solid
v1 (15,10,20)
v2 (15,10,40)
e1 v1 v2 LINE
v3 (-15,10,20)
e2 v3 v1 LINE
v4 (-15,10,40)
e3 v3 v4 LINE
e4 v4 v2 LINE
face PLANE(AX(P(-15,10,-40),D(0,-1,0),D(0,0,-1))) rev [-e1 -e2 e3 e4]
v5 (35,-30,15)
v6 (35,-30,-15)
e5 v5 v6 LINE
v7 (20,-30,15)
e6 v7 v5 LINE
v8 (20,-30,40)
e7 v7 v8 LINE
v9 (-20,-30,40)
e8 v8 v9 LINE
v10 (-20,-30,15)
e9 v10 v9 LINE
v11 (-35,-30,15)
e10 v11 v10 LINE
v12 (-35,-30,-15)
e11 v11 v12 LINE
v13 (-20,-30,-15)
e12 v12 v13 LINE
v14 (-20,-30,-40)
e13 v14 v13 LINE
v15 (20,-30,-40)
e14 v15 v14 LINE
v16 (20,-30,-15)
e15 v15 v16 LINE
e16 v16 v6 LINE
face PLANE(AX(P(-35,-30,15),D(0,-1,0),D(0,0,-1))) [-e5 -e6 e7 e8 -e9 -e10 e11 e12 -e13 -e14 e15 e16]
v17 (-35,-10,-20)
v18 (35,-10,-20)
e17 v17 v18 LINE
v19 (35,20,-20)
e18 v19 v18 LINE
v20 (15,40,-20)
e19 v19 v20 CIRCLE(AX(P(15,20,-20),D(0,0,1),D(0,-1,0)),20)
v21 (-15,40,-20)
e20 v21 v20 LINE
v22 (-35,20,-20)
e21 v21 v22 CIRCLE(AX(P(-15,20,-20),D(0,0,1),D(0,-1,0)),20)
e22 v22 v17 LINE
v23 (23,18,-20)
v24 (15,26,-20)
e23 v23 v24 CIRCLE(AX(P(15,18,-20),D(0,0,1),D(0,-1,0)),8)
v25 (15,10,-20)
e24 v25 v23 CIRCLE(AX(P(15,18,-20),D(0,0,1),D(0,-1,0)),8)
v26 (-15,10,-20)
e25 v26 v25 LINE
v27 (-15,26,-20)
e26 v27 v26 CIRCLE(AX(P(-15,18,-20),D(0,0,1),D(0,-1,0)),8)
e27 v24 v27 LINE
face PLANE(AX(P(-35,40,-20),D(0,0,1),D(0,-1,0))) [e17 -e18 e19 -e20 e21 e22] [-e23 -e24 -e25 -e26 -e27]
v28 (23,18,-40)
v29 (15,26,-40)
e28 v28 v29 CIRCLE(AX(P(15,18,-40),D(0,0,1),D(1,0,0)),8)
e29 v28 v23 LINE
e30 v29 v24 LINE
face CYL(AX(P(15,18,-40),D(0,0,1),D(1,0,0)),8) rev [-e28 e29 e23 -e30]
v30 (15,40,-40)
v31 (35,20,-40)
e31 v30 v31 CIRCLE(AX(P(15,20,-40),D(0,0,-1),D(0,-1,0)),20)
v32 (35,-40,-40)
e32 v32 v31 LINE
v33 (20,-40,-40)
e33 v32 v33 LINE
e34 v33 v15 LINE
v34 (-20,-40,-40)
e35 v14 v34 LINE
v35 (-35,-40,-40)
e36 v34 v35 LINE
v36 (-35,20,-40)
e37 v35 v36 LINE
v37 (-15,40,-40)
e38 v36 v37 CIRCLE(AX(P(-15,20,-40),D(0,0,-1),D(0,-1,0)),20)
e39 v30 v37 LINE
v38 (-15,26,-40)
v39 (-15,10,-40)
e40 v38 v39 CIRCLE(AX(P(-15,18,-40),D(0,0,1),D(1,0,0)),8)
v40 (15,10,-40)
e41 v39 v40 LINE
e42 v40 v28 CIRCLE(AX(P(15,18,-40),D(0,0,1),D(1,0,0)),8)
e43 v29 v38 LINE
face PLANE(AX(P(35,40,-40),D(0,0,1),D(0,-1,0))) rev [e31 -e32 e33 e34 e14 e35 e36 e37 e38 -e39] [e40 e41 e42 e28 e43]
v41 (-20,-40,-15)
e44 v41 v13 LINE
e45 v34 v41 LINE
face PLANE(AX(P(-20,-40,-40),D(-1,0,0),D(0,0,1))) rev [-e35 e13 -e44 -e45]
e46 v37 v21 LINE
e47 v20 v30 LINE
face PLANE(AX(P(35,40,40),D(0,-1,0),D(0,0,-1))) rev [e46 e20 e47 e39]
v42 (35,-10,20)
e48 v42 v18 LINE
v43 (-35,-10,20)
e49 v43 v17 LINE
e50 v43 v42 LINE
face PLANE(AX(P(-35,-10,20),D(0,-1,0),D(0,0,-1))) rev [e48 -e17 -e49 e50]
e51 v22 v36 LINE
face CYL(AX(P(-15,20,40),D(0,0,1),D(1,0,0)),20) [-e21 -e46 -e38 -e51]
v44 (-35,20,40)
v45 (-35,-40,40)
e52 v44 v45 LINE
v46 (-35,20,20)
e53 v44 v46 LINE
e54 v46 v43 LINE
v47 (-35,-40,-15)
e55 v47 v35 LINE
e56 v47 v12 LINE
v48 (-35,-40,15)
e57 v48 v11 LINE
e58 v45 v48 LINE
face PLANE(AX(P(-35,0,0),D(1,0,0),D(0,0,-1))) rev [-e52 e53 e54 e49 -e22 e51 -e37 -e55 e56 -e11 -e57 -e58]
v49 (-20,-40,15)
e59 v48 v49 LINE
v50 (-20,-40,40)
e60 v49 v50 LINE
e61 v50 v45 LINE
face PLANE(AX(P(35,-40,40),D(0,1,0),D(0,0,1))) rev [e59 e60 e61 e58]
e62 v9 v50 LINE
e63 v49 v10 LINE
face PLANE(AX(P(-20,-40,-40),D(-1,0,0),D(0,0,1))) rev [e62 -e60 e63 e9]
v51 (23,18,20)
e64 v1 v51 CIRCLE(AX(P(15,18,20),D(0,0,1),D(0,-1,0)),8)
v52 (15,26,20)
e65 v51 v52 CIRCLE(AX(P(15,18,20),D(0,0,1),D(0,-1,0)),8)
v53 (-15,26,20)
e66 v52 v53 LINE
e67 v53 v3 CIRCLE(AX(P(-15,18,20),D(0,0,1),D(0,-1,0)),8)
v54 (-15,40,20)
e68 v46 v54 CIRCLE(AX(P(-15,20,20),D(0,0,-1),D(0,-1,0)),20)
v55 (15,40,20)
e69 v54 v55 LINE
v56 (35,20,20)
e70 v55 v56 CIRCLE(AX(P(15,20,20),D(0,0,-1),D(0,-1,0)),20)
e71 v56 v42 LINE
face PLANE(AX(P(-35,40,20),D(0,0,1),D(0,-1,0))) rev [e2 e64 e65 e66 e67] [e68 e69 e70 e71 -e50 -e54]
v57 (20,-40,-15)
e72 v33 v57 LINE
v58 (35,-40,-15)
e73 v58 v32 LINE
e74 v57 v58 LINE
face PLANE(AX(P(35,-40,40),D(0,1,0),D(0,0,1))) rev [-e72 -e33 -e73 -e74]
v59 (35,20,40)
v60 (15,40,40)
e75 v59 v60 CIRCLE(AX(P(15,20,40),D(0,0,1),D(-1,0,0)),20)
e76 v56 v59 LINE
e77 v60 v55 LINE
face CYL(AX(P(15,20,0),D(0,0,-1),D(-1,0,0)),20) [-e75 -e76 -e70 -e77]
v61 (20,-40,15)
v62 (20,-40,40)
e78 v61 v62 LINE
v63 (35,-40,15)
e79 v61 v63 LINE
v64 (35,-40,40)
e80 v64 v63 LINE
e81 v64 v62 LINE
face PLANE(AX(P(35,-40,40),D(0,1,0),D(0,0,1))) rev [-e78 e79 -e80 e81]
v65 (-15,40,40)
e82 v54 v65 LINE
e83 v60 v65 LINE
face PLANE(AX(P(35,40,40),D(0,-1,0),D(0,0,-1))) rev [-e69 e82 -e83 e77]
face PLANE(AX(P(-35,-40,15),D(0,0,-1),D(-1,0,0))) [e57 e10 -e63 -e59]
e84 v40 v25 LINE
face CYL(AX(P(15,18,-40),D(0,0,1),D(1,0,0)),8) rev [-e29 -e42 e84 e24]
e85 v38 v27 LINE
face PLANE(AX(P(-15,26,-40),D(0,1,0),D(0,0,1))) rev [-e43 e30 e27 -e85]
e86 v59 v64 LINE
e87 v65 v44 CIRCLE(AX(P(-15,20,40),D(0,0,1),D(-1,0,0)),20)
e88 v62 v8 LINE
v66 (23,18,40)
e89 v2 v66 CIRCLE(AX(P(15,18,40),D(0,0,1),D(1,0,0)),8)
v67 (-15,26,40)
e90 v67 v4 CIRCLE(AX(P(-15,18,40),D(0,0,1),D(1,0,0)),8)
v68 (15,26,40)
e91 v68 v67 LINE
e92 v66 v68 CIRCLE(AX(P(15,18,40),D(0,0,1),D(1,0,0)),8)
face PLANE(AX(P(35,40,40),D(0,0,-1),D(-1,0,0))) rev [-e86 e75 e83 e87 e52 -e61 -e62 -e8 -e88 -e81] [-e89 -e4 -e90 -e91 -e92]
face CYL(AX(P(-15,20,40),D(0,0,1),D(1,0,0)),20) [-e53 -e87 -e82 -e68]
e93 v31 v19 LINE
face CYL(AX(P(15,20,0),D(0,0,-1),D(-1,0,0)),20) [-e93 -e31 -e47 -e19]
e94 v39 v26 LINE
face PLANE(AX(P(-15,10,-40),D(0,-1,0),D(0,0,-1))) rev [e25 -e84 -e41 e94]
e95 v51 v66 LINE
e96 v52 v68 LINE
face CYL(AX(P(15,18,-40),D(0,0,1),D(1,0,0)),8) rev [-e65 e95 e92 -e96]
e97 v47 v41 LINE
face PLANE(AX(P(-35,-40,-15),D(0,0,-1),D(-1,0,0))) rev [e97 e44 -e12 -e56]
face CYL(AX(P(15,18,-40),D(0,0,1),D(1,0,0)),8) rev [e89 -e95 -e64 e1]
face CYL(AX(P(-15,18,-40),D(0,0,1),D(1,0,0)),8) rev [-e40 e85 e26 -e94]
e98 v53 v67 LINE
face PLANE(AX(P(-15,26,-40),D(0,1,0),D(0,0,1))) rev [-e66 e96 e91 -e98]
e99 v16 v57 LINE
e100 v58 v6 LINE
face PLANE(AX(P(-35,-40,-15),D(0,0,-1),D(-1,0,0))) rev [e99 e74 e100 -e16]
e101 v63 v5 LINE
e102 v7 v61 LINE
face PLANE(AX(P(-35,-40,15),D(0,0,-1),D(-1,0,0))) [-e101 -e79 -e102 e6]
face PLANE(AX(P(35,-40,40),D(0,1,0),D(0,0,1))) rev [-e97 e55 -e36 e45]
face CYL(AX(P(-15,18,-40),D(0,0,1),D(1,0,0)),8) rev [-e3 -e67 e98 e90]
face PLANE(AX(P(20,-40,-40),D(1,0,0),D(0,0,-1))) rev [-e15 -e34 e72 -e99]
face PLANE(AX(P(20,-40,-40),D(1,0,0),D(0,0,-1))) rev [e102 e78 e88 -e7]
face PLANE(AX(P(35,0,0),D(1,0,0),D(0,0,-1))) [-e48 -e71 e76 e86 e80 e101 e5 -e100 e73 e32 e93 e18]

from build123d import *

# Parameters (mm, degrees)
BASE_BLOCK_PROFILE_80X80_W  = 80
BASE_BLOCK_PROFILE_80X80_H  = 80
BASE_BLOCK_80X80X70_DEPTH   = 35
NOTCH_CUT_20X20_DEPTH       = 91
NOTCH_CUT_20X20_DEPTH_BACK  = 91
NOTCH_PROFILE_20X20_W       = 40
NOTCH_PROFILE_20X20_H       = 50
NOTCH_CUT_25X25_DEPTH       = 91
NOTCH_CUT_25X25_DEPTH_BACK  = 91
NOTCH_PROFILE_25X25_W       = 30
NOTCH_PROFILE_25X25_H       = 10
POCKET_CUT_40X15_DEPTH      = 97.046863561
POCKET_CUT_40X15_DEPTH_BACK = 97.046863561
POCKET_PROFILE_40X15_W      = 40
POCKET_PROFILE_40X15_H      = 10
UPRIGHT_SLOT_CUT_DEPTH      = 97.046863561
UPRIGHT_SLOT_CUT_DEPTH_BACK = 97.046863561
UPRIGHT_TOP_FILLETS_R20_R   = 20


with BuildPart() as part:
    # Base Block Profile 80x80 → Base Block 80x80x70 (new, symmetric)
    with BuildSketch(Plane(origin=(0, 0, 0), x_dir=(0, 0, -1), z_dir=(1, 0, 0))):
        Rectangle(BASE_BLOCK_PROFILE_80X80_W, BASE_BLOCK_PROFILE_80X80_H)
    extrude(amount=BASE_BLOCK_80X80X70_DEPTH, both=True)

    # Notch Profile 20x20 → Notch Cut 20x20 (cut, two sides: drawn at the far end of the back side and taken through both)
    with BuildSketch(Plane(origin=(35, 0, 0), x_dir=(0, 0, -1), z_dir=(1, 0, 0)).offset(-NOTCH_CUT_20X20_DEPTH_BACK)):
        with Locations((0, 15)):
            Rectangle(NOTCH_PROFILE_20X20_W, NOTCH_PROFILE_20X20_H)
    extrude(amount=NOTCH_CUT_20X20_DEPTH + NOTCH_CUT_20X20_DEPTH_BACK, mode=Mode.SUBTRACT)

    # Notch Profile 25x25 → Notch Cut 25x25 (cut, two sides: drawn at the far end of the back side and taken through both)
    with BuildSketch(Plane(origin=(35, 0, 0), x_dir=(0, 0, -1), z_dir=(1, 0, 0)).offset(-NOTCH_CUT_25X25_DEPTH_BACK)):
        with Locations((0, -35)):
            Rectangle(NOTCH_PROFILE_25X25_W, NOTCH_PROFILE_25X25_H)
    extrude(amount=NOTCH_CUT_25X25_DEPTH + NOTCH_CUT_25X25_DEPTH_BACK, mode=Mode.SUBTRACT)

    # Pocket Profile 40x15 → Pocket Cut 40x15 (cut, two sides: drawn at the far end of the back side and taken through both)
    with BuildSketch(Plane.XY.offset(40).offset(-POCKET_CUT_40X15_DEPTH_BACK)):
        with Locations((0, -35)):
            Rectangle(POCKET_PROFILE_40X15_W, POCKET_PROFILE_40X15_H)
    extrude(amount=POCKET_CUT_40X15_DEPTH + POCKET_CUT_40X15_DEPTH_BACK, mode=Mode.SUBTRACT)

    # Upright Slot Profile → Upright Slot Cut (cut, two sides: drawn at the far end of the back side and taken through both)
    with BuildSketch(Plane.XY.offset(40).offset(-UPRIGHT_SLOT_CUT_DEPTH_BACK)):
        with BuildLine():
            Line((-15, 26), (15, 26))
            ThreePointArc((15, 26), (23, 18), (15, 10))
            Line((15, 10), (-15, 10))
            ThreePointArc((-15, 10), (-23, 18), (-15, 26))
        make_face()
    extrude(amount=UPRIGHT_SLOT_CUT_DEPTH + UPRIGHT_SLOT_CUT_DEPTH_BACK, mode=Mode.SUBTRACT)

    # Upright Top Fillets R20
    upright_top_fillets_r20_edges = [part.edges().sort_by_distance(p)[0] for p in [
        (-35, 40, 30),
        (35, 40, 30),
        (-35, 40, -30),
        (35, 40, -30),
    ]]
    fillet(upright_top_fillets_r20_edges, radius=UPRIGHT_TOP_FILLETS_R20_R)


solid = part.part
